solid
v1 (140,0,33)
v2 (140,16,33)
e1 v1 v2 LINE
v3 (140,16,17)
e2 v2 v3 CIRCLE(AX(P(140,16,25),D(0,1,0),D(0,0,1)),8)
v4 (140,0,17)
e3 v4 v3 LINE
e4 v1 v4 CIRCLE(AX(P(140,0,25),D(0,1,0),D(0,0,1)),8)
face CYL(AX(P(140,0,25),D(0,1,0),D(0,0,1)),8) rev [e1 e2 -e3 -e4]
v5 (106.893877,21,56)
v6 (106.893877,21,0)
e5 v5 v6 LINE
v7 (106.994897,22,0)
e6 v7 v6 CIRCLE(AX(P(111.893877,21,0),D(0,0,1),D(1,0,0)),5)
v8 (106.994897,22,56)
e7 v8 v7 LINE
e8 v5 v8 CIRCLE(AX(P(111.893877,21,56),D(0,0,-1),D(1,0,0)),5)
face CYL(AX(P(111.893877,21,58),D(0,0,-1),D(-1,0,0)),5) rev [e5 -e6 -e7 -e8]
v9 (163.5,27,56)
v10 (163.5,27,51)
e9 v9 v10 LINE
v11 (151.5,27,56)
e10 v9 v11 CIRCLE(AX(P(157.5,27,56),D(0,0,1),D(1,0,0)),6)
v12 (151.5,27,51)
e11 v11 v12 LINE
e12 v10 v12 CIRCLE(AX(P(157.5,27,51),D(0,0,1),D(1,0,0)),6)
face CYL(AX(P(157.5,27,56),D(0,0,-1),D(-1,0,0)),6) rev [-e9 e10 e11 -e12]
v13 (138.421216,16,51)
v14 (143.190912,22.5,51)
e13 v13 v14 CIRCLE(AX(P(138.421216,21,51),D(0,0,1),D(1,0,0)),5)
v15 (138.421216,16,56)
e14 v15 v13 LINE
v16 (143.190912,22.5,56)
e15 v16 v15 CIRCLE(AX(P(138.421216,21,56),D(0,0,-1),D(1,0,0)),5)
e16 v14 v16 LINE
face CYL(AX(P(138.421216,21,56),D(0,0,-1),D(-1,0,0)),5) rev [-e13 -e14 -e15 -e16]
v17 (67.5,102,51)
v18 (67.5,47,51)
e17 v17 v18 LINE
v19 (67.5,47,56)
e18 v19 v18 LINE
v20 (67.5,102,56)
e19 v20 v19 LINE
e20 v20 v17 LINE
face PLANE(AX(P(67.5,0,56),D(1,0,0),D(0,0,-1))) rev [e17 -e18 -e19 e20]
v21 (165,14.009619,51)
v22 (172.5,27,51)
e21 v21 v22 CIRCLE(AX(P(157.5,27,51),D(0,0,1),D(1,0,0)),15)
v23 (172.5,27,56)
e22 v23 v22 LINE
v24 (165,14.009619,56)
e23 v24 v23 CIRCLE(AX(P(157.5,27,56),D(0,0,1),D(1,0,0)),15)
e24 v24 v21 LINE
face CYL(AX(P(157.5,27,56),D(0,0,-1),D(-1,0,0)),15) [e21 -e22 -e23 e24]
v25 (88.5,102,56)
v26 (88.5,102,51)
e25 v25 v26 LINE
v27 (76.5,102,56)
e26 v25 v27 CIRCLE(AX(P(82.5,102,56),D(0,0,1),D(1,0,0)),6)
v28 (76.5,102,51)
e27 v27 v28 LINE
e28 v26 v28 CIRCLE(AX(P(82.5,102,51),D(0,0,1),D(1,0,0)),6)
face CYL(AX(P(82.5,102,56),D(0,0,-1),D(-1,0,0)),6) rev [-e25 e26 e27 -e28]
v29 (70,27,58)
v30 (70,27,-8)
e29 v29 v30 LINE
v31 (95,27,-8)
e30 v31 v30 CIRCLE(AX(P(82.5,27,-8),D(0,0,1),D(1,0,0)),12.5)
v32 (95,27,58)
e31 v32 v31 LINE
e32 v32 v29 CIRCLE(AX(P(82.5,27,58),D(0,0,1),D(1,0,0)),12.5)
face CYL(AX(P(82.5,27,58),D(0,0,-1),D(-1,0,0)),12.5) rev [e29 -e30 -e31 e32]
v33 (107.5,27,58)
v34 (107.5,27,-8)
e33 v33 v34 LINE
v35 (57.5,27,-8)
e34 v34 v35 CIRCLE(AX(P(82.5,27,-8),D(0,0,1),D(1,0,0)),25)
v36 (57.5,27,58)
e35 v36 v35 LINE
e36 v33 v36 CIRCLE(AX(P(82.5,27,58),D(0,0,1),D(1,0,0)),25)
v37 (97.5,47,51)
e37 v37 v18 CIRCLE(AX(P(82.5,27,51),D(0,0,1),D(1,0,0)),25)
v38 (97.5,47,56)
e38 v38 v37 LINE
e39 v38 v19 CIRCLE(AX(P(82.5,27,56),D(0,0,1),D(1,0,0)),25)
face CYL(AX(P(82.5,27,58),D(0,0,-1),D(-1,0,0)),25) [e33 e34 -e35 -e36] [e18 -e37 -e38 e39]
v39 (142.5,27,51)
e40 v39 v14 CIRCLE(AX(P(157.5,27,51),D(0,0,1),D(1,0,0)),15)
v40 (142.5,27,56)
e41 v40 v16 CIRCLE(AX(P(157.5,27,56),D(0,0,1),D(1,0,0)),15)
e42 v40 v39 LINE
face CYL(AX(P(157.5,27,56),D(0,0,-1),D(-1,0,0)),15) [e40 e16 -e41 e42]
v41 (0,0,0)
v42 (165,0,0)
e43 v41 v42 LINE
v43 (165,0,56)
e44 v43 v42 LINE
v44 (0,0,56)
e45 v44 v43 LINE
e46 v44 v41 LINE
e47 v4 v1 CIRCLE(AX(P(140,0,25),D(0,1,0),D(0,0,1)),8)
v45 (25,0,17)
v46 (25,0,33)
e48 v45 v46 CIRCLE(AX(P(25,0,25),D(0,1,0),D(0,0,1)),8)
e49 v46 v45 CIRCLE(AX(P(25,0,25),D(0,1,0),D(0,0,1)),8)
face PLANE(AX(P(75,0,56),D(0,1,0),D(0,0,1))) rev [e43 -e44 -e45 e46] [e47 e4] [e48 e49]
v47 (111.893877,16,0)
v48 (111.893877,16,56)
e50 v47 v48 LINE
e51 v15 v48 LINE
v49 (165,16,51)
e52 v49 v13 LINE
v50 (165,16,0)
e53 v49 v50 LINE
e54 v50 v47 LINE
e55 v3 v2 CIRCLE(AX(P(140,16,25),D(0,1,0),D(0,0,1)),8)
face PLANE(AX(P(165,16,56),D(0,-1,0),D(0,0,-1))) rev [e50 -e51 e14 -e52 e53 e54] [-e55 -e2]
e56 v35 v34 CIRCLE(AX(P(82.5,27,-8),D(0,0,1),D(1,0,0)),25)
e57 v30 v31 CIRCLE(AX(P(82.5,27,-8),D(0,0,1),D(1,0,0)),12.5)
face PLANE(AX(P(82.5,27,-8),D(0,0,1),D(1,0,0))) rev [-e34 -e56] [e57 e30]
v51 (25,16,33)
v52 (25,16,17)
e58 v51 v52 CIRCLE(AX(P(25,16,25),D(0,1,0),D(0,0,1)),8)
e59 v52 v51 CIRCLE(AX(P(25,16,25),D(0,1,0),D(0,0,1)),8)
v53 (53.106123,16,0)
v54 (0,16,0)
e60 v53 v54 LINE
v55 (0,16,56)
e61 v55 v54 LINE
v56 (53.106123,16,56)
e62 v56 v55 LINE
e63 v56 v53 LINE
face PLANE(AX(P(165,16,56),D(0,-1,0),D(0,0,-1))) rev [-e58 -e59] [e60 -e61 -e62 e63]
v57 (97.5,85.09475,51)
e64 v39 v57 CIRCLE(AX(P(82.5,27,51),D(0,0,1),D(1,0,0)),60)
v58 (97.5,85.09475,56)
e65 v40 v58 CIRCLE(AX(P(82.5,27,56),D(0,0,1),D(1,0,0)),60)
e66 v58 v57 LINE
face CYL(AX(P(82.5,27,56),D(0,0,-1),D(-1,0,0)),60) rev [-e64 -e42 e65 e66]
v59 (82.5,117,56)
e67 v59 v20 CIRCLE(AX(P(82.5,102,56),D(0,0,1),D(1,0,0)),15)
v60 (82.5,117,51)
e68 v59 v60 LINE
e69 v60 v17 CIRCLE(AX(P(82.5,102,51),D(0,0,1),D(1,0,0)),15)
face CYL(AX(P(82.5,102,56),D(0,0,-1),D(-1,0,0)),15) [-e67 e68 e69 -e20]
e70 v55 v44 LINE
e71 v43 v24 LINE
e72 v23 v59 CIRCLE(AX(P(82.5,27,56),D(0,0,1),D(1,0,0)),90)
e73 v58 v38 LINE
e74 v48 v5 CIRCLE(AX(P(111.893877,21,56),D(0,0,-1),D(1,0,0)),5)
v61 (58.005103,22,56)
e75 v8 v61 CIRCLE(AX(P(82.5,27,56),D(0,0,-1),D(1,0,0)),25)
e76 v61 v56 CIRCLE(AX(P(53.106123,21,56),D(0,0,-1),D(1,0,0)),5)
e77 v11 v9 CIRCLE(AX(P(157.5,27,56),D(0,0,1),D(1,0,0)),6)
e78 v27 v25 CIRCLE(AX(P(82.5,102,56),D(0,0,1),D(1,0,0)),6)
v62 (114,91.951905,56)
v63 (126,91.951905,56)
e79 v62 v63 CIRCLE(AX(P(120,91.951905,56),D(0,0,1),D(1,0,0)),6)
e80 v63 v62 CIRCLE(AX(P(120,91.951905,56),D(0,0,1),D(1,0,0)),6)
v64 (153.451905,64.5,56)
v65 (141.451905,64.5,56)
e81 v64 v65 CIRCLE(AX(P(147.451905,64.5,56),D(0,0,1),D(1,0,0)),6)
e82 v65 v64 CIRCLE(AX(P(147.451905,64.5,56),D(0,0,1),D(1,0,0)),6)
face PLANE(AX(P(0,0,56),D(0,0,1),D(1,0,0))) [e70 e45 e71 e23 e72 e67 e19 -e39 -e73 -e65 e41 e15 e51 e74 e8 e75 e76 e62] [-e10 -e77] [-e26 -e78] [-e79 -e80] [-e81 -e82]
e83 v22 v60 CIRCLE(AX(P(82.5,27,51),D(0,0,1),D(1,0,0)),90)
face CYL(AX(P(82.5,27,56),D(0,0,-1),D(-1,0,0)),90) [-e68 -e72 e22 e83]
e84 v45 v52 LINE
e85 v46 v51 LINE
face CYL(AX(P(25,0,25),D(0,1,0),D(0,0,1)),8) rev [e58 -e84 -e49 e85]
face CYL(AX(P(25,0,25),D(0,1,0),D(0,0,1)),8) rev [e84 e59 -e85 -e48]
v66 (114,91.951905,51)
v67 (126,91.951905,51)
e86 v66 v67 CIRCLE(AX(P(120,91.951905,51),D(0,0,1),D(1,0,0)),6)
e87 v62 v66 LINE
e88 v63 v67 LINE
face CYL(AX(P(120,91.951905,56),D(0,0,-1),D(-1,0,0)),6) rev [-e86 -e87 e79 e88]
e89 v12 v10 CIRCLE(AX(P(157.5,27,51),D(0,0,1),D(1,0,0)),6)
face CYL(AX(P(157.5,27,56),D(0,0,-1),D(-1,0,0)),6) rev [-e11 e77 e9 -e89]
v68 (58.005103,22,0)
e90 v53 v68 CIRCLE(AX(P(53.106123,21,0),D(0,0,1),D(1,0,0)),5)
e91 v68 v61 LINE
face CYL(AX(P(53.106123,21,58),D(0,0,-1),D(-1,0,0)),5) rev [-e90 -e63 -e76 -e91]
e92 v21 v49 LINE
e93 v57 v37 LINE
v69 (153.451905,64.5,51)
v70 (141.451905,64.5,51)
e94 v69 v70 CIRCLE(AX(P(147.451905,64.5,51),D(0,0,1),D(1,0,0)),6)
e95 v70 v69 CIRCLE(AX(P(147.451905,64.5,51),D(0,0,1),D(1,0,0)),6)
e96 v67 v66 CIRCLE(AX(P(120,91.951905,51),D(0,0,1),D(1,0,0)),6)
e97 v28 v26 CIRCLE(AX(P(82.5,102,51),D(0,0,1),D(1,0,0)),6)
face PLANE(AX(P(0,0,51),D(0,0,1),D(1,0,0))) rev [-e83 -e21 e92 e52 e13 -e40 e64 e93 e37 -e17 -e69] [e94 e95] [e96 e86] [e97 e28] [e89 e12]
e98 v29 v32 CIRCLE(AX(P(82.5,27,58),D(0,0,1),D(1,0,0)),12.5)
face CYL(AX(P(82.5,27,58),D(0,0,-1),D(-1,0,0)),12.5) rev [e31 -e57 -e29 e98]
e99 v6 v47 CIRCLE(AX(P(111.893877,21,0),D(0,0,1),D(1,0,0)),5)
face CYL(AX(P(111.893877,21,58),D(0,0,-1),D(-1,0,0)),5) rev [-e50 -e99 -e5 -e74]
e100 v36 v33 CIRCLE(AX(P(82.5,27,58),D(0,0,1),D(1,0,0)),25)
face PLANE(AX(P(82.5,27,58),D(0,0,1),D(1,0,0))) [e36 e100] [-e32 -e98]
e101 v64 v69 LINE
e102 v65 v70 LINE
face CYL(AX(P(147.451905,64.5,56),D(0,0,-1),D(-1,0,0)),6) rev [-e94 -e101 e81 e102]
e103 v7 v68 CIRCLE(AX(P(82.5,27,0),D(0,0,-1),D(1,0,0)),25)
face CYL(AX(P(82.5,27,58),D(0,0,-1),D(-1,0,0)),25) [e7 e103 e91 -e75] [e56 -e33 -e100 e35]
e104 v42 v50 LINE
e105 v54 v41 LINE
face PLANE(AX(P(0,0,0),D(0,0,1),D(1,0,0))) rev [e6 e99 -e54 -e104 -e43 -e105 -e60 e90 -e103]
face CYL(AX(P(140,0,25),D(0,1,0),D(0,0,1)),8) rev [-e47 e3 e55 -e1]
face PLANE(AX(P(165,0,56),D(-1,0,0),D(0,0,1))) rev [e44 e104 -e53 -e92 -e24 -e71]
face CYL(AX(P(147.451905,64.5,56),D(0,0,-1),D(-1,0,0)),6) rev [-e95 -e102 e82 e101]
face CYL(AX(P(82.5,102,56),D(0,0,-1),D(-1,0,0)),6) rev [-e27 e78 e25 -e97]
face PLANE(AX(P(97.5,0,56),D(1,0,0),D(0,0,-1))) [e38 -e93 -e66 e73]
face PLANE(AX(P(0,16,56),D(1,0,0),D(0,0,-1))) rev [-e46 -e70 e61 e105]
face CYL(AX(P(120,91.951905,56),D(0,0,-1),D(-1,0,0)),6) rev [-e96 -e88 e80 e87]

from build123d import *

# Parameters (mm, degrees)
BASE_PLATE_DEPTH               = 56
HUB_BOSS_PROFILE_R             = 25
HUB_BOSS_PROFILE_R_2           = 12.5
HUB_BOSS_27_DEPTH              = 33
HUB_BORE_PROFILE_R             = 12.5
HUB_BORE_DEPTH                 = 186.162091153
FLANGE_START                   = 5
FLANGE_PLATE_PROFILE_R         = 6
FLANGE_PLATE_DEPTH             = 5
BASE_MOUNTING_HOLE_1_PROFILE_R = 8
BASE_MOUNTING_HOLE_1_DEPTH     = 209.137574695
BASE_MOUNTING_HOLE_2_PROFILE_R = 8
BASE_MOUNTING_HOLE_2_DEPTH     = 209.137574695
HUB_TO_BASE_FILLET_R5_R        = 5
FLANGE_FILLET_R5_R             = 5


with BuildPart() as part:
    # Base Plate Profile → Base Plate (new body)
    with BuildSketch(Plane.XY):
        Polygon((0, 0), (75, 0), (165, 0), (165, 16), (0, 16), align=None)
    extrude(amount=BASE_PLATE_DEPTH)

    # Hub Boss Profile → Hub Boss Ø27 (add, symmetric)
    with BuildSketch(Plane.XY.offset(25)):
        with Locations((82.5, 27)):
            Circle(HUB_BOSS_PROFILE_R)
        with Locations((82.5, 27)):
            Circle(HUB_BOSS_PROFILE_R_2, mode=Mode.SUBTRACT)
    extrude(amount=HUB_BOSS_27_DEPTH, both=True)

    # Hub Bore Profile → Hub Bore (cut, through all)
    with BuildSketch(Plane.XY.offset(58)):
        with Locations((82.5, 27)):
            Circle(HUB_BORE_PROFILE_R)
    extrude(amount=-HUB_BORE_DEPTH, mode=Mode.SUBTRACT)

    # Flange Plate Profile → Flange Plate (add)
    # profile 1 of 2: a face of its own
    with BuildSketch(Plane.XY.offset(51).offset(FLANGE_START)):
        with BuildLine():
            ThreePointArc((82.5, 87), (71.893398282, 91.393398282), (67.5, 102))
            Line((67.5, 102), (67.5, 47))
            ThreePointArc((67.5, 47), (82.5, 52), (97.5, 47))
            Line((97.5, 47), (97.5, 85.094750193))
            ThreePointArc((97.5, 85.094750193), (90.060257549, 86.521781776), (82.5, 87))
        make_face()
    # profile 2 of 2: a face of its own
    with BuildSketch(Plane.XY.offset(51).offset(FLANGE_START)):
        with BuildLine():
            ThreePointArc((142.5, 27), (124.926406871, 69.426406871), (82.5, 87))
            ThreePointArc((82.5, 87), (67.5, 102), (82.5, 117))
            ThreePointArc((82.5, 117), (146.139610307, 90.639610307), (172.5, 27))
            ThreePointArc((172.5, 27), (157.5, 12), (142.5, 27))
        make_face()
        with Locations((120, 91.951905284)):
            Circle(FLANGE_PLATE_PROFILE_R, mode=Mode.SUBTRACT)
        with Locations((147.451905284, 64.5)):
            Circle(FLANGE_PLATE_PROFILE_R, mode=Mode.SUBTRACT)
        with Locations((157.5, 27)):
            Circle(FLANGE_PLATE_PROFILE_R, mode=Mode.SUBTRACT)
        with Locations((82.5, 102)):
            Circle(FLANGE_PLATE_PROFILE_R, mode=Mode.SUBTRACT)
    extrude(amount=-FLANGE_PLATE_DEPTH)

    # Base Mounting Hole 1 Profile → Base Mounting Hole 1 (cut, through all)
    with BuildSketch(Plane(origin=(0, 16, 0), x_dir=(1, 0, 0), z_dir=(0, 1, 0))):
        with Locations(Location((25, -25, 0), (0, 0, 270))):
            Circle(BASE_MOUNTING_HOLE_1_PROFILE_R)
    extrude(amount=-BASE_MOUNTING_HOLE_1_DEPTH, mode=Mode.SUBTRACT)

    # Base Mounting Hole 2 Profile → Base Mounting Hole 2 (cut, through all)
    with BuildSketch(Plane(origin=(0, 16, 0), x_dir=(1, 0, 0), z_dir=(0, 1, 0))):
        with Locations(Location((140, -25, 0), (0, 0, 270))):
            Circle(BASE_MOUNTING_HOLE_2_PROFILE_R)
    extrude(amount=-BASE_MOUNTING_HOLE_2_DEPTH, mode=Mode.SUBTRACT)

    # Hub to Base Fillet R5
    hub_to_base_fillet_r5_edges = [part.edges().sort_by_distance(p)[0] for p in [
        (60.050055679, 16, 28),
    ]]
    fillet(hub_to_base_fillet_r5_edges, radius=HUB_TO_BASE_FILLET_R5_R)

    # Flange Fillet R5
    flange_fillet_r5_edges = [part.edges().sort_by_distance(p)[0] for p in [
        (104.949944321, 16, 28),
        (147.301960973, 16, 53.5),
    ]]
    fillet(flange_fillet_r5_edges, radius=FLANGE_FILLET_R5_R)


solid = part.part
